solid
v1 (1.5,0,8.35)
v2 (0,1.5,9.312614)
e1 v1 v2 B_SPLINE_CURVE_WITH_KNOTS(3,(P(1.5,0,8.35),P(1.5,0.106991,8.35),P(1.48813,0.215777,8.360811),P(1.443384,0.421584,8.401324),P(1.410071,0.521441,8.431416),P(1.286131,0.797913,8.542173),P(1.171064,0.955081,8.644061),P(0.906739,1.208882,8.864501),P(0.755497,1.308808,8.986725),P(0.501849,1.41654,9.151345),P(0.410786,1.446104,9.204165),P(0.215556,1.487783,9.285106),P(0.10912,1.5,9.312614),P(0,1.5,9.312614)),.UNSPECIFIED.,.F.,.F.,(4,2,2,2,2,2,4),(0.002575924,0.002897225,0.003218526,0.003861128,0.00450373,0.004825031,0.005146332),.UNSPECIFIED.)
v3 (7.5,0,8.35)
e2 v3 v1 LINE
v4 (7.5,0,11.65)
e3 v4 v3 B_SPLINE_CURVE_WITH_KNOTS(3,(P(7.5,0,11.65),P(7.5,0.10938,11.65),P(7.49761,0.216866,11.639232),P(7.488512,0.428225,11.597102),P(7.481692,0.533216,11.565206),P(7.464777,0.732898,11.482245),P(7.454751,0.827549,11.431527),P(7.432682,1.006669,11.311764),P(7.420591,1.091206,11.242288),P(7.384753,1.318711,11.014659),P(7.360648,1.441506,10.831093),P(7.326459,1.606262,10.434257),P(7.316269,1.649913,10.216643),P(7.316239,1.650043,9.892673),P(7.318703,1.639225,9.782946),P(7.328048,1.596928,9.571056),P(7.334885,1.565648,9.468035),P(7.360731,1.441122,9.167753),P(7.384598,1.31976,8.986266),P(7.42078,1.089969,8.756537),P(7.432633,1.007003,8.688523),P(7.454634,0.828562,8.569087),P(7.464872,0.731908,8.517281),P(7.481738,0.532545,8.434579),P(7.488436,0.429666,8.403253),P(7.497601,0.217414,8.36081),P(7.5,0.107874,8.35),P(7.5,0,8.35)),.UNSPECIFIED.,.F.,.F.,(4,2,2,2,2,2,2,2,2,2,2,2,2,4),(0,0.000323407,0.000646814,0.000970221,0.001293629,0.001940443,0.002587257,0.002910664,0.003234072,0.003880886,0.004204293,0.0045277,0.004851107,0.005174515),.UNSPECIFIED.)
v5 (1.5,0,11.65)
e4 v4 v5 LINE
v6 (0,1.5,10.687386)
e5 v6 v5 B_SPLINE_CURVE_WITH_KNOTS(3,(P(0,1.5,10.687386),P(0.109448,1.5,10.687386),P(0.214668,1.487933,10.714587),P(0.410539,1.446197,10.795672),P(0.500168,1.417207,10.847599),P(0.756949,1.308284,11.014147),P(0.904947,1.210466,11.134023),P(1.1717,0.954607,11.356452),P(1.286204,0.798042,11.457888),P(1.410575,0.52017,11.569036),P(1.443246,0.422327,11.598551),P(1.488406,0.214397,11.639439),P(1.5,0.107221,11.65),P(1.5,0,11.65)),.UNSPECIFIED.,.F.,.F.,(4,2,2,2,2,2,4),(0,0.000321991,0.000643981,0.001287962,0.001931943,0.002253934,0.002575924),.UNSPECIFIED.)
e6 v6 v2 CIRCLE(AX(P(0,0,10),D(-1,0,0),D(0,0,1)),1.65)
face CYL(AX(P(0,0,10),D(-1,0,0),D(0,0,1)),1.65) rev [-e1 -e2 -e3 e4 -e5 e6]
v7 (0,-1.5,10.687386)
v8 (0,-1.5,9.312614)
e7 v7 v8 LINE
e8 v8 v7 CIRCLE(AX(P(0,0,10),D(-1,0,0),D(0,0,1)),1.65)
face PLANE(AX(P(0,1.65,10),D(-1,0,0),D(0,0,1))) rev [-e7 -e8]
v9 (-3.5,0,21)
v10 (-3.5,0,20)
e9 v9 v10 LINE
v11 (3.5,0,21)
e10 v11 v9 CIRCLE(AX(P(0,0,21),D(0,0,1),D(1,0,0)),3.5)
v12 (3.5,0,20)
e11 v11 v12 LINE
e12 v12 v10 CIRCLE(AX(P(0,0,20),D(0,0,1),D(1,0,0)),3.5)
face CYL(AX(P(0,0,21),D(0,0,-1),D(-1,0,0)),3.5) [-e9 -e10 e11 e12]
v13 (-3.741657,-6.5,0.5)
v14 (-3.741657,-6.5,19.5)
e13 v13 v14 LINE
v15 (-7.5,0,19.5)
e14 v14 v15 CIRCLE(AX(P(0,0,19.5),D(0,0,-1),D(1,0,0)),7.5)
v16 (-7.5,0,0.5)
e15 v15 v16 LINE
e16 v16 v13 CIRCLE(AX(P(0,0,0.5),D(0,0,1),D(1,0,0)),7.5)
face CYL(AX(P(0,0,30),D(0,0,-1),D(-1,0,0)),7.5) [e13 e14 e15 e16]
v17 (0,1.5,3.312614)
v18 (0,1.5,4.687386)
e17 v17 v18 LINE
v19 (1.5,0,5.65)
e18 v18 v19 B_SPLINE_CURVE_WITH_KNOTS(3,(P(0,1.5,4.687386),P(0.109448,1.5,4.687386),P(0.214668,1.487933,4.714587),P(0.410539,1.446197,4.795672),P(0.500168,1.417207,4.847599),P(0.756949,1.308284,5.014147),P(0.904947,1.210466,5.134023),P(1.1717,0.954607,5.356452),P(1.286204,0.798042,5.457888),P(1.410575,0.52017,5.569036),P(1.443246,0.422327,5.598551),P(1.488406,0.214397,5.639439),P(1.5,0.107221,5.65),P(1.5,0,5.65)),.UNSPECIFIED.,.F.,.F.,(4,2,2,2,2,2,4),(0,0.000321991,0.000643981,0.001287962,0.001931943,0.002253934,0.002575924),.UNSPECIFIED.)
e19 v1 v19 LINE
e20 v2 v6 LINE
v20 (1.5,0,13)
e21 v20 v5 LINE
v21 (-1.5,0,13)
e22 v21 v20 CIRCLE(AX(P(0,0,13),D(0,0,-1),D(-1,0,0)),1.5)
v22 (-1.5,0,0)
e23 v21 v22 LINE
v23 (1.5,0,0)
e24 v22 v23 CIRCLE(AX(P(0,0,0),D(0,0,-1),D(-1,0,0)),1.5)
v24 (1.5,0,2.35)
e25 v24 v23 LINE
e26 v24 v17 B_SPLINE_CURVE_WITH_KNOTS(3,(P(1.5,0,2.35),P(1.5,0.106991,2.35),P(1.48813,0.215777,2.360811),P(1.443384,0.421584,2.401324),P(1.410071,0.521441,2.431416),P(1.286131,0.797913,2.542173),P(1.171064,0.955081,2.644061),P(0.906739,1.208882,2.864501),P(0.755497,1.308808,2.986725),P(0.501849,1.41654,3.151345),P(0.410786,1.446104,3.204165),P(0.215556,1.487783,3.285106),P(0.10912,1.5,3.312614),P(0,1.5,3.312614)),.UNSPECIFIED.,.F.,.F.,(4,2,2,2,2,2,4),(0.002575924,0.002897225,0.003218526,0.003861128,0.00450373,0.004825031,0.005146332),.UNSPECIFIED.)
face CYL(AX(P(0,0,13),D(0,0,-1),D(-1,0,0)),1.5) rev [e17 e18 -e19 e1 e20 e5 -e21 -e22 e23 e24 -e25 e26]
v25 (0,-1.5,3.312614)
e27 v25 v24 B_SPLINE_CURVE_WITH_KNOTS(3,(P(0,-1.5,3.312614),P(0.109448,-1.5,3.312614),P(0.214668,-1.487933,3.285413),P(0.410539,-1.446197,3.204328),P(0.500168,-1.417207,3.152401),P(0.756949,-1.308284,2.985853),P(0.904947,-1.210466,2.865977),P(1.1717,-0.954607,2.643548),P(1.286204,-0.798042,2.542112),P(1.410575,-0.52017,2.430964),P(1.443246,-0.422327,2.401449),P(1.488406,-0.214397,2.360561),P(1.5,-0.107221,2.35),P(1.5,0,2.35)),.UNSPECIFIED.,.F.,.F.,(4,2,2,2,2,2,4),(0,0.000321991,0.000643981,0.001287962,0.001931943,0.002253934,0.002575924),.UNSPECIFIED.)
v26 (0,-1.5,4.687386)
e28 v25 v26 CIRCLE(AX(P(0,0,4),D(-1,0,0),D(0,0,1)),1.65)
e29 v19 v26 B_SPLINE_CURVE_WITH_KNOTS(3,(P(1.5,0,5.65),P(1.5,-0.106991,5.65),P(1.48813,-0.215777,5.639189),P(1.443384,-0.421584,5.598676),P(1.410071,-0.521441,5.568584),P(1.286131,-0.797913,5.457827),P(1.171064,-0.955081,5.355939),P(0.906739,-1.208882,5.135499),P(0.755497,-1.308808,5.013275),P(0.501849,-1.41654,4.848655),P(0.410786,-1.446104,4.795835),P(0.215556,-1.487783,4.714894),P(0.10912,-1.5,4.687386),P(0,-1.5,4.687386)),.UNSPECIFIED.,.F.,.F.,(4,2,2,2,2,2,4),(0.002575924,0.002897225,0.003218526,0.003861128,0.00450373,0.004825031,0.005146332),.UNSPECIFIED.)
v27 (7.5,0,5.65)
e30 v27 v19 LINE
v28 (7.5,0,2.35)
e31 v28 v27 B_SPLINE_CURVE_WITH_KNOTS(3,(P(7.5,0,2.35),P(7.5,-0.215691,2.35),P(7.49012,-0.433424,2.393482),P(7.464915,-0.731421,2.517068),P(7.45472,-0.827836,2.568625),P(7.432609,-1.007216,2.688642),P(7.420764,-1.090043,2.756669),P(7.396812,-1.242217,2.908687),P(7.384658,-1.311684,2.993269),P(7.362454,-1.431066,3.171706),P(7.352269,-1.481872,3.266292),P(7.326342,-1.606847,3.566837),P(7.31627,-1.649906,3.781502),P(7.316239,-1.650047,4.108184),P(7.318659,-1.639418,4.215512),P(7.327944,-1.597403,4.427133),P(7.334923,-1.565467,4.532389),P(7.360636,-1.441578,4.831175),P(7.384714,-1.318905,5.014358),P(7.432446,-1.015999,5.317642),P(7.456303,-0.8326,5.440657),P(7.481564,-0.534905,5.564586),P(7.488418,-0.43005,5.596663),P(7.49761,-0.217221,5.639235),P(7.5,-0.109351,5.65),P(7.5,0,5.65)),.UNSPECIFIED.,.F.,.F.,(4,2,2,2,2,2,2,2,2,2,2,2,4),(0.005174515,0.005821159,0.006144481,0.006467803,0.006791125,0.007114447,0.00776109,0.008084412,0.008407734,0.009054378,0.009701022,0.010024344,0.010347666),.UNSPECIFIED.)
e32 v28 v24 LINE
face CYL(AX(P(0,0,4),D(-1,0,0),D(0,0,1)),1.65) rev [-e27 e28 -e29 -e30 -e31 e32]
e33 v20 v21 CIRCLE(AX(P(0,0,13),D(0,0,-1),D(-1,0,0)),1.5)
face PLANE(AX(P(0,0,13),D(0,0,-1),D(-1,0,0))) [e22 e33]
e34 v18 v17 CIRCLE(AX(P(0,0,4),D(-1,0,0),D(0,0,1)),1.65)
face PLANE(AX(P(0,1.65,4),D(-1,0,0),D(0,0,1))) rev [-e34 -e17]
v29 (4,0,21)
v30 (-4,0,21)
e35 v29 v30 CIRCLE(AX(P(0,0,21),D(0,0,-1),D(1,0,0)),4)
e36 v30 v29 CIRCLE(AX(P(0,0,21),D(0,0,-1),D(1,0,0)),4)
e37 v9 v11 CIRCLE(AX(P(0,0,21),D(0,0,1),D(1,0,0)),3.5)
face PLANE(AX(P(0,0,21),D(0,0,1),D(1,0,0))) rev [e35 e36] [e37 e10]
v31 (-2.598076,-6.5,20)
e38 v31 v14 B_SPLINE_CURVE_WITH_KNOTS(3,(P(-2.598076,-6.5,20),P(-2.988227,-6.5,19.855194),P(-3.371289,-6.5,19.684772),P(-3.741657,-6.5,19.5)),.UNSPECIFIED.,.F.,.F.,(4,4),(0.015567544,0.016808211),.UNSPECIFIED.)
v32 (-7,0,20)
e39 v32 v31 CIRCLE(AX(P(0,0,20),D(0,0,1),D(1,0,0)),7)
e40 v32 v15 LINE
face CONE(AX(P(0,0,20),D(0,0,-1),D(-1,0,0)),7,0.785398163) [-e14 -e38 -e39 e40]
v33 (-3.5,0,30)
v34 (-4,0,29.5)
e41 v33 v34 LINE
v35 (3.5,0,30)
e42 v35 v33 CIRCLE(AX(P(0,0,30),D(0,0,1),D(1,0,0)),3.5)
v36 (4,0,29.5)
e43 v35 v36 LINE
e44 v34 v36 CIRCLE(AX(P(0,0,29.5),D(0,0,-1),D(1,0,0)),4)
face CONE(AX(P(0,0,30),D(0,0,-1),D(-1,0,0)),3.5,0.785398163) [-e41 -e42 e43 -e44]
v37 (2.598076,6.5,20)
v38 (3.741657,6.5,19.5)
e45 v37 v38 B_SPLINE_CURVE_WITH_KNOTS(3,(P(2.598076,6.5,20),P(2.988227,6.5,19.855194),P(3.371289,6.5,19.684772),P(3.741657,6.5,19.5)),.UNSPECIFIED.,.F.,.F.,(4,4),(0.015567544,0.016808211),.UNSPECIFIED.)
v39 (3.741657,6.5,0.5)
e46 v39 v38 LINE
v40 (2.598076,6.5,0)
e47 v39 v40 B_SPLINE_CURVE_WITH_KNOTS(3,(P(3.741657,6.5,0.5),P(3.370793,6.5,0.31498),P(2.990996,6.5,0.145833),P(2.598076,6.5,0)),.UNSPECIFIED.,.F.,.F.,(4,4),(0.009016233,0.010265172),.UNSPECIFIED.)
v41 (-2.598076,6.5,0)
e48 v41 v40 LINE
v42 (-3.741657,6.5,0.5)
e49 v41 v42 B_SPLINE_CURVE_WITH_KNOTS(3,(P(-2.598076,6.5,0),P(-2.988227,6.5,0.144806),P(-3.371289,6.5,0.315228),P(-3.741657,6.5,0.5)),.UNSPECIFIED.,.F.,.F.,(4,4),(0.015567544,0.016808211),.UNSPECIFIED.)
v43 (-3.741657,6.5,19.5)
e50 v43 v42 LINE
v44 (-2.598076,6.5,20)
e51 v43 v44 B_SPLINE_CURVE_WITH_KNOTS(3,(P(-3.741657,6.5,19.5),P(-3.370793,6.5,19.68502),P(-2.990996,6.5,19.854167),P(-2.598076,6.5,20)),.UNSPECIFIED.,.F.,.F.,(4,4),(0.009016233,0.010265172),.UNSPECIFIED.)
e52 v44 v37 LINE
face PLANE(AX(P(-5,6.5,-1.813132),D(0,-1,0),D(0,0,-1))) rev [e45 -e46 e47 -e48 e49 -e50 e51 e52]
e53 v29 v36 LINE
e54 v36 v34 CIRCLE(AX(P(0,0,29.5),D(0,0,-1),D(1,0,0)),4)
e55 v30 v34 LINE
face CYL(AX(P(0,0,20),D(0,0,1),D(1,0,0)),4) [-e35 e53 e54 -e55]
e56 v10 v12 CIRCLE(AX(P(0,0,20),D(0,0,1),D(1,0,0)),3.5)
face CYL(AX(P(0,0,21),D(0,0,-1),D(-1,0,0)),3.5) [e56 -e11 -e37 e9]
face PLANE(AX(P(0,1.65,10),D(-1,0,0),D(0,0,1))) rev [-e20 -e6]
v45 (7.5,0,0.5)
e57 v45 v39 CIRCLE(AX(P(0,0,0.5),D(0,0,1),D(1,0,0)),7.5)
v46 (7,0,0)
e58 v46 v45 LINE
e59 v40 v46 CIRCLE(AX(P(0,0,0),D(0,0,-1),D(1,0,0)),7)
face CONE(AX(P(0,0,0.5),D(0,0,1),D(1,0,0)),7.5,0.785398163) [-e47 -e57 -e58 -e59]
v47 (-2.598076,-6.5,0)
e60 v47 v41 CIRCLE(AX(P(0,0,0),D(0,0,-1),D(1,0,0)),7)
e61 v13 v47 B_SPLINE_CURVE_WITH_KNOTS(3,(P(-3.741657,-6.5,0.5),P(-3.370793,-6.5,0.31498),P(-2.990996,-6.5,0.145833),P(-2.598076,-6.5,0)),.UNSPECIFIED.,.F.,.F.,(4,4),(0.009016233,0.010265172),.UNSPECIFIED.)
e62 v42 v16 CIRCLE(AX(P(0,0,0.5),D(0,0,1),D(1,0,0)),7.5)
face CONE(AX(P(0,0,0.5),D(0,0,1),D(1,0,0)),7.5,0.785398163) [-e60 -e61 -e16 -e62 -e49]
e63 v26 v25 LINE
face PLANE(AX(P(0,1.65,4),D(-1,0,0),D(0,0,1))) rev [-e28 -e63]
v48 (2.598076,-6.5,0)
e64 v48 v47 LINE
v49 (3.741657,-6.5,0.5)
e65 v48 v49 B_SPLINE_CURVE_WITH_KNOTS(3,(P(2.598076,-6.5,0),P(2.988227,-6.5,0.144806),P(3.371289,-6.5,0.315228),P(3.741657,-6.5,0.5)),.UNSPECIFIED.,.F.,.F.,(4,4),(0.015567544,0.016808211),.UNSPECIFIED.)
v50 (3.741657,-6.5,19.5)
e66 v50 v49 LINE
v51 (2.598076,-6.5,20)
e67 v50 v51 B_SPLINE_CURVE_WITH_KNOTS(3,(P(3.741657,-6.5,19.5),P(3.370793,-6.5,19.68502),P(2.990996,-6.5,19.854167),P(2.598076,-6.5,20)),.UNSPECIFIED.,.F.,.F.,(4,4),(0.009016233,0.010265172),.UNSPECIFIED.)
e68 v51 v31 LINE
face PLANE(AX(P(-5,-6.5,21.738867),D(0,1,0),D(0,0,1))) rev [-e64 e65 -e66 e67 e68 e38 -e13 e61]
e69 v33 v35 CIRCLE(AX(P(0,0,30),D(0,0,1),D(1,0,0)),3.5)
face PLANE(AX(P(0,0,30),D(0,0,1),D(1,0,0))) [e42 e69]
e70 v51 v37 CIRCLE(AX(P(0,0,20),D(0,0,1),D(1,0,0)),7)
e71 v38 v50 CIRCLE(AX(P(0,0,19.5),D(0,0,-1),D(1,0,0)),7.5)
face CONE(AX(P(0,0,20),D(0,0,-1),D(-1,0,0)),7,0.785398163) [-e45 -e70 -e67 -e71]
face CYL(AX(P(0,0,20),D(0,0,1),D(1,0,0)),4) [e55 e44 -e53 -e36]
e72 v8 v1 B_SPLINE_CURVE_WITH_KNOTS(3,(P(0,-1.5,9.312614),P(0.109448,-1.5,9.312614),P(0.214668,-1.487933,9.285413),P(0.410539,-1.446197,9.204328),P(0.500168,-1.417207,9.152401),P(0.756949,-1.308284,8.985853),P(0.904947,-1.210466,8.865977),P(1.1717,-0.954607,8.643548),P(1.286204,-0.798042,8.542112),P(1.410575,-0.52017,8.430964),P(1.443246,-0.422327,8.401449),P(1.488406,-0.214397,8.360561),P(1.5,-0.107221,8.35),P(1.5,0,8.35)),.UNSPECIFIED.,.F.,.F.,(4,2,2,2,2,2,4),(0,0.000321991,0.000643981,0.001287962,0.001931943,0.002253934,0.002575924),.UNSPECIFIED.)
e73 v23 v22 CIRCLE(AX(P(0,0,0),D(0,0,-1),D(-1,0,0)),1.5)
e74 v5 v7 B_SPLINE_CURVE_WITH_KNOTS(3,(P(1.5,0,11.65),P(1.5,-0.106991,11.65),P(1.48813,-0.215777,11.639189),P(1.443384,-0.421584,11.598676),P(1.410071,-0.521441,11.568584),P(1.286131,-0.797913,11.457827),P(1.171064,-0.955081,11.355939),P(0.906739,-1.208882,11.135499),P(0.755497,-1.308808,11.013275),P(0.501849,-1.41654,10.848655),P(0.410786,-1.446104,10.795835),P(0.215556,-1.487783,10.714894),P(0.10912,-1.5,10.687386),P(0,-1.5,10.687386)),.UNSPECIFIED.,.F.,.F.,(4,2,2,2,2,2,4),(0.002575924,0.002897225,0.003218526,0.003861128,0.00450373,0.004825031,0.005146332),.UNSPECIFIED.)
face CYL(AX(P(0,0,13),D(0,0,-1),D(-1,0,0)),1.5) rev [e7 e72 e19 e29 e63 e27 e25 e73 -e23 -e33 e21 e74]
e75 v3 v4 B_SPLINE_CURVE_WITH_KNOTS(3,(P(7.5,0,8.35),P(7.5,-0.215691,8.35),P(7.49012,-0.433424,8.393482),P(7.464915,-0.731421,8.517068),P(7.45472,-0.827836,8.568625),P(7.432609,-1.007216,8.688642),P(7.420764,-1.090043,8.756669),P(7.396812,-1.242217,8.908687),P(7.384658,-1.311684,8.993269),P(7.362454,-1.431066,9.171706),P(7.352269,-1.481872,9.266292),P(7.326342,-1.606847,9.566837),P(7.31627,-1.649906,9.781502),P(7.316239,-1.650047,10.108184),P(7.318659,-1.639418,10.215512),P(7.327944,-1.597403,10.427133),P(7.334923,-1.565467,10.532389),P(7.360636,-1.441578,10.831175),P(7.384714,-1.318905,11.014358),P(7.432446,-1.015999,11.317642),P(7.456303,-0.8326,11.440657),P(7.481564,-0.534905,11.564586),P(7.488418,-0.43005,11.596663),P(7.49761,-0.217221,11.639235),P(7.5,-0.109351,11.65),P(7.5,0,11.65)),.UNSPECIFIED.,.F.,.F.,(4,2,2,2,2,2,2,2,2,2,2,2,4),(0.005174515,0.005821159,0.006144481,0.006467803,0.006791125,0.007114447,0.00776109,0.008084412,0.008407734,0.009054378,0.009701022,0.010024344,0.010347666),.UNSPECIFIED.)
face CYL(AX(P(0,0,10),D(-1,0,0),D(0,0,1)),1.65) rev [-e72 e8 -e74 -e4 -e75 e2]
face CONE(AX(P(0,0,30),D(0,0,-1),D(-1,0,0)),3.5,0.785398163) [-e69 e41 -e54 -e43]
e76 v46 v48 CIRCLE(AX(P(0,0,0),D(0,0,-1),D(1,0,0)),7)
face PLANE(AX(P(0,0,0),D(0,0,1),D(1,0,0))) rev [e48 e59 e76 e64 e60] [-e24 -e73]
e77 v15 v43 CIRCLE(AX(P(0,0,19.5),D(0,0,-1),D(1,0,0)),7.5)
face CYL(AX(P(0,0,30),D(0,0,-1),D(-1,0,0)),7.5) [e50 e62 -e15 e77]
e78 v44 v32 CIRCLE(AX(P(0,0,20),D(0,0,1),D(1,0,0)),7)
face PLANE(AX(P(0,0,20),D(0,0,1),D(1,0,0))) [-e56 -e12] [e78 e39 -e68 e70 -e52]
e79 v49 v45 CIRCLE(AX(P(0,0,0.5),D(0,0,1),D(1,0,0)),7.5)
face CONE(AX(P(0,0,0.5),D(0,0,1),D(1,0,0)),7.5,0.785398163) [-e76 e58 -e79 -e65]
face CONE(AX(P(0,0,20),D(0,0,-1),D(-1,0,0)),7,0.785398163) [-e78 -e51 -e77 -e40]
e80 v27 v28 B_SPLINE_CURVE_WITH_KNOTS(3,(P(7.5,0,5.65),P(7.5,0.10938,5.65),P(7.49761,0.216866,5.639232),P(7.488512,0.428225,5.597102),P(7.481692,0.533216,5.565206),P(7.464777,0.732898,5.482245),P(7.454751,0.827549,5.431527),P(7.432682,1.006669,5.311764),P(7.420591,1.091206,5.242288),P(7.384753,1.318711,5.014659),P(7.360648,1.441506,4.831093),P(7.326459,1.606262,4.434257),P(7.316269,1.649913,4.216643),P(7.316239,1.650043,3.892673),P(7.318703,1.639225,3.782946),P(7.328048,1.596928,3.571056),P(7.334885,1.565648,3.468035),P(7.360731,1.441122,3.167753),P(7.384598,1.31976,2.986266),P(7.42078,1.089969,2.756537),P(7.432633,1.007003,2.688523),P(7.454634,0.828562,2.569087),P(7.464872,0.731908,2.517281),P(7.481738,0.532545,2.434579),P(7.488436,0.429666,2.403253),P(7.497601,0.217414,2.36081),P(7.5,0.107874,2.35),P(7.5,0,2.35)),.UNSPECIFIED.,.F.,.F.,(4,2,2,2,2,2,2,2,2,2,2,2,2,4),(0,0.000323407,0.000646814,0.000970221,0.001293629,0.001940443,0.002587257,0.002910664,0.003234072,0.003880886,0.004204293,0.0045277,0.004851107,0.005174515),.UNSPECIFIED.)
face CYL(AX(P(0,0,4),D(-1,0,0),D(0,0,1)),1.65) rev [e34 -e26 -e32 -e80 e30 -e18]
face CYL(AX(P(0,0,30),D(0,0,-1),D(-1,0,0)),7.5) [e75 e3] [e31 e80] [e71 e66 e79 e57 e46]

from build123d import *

# Parameters (mm, degrees)
SKETCH_1_R                  = 7.5
EXTRUDE_1_DEPTH             = 30
SKETCH_2_R                  = 8.226284638
SKETCH_2_R_2                = 4
CUT_EXTRUDE_1_DEPTH         = 10
SKETCH_3_R                  = 1.5
CUT_EXTRUDE_2_DEPTH         = 13
SKETCH_4_R                  = 4.479492859
SKETCH_4_R_2                = 3.5
CUT_EXTRUDE_3_DEPTH         = 1
CHAMFER_1_SIZE              = 0.5
SKETCH_6_W                  = 1.65
SKETCH_6_H                  = 7.5
HOLE_WIZARD_M4_1_AT_2_COUNT = 2
HOLE_WIZARD_M4_1_AT_2_PITCH = 6
SKETCH_7_W                  = 26.910087363
SKETCH_7_H                  = 4.855614415
SKETCH_7_W_2                = 23.143582724
SKETCH_7_H_2                = 3.131190604
CUT_EXTRUDE_4_DEPTH         = 5


with BuildPart() as part:
    # 草图1 → 凸台-拉伸1 (new body)
    with BuildSketch(Plane.XY):
        Circle(SKETCH_1_R)
    extrude(amount=EXTRUDE_1_DEPTH)

    # 草图2 → 切除-拉伸1 (cut)
    with BuildSketch(Plane.XY.offset(30)):
        Circle(SKETCH_2_R)
        Circle(SKETCH_2_R_2, mode=Mode.SUBTRACT)
    extrude(amount=-CUT_EXTRUDE_1_DEPTH, mode=Mode.SUBTRACT)

    # 草图3 → 切除-拉伸2 (cut)
    with BuildSketch(Plane(origin=(0, 0, 0), x_dir=(-1, 0, 0), z_dir=(0, 0, -1))):
        Circle(SKETCH_3_R)
    extrude(amount=-CUT_EXTRUDE_2_DEPTH, mode=Mode.SUBTRACT)

    # 草图4 → 切除-拉伸3 (cut)
    with BuildSketch(Plane.XY.offset(20)):
        Circle(SKETCH_4_R)
        Circle(SKETCH_4_R_2, mode=Mode.SUBTRACT)
    extrude(amount=CUT_EXTRUDE_3_DEPTH, mode=Mode.SUBTRACT)

    # 倒角1
    chamfer_1_edges = [part.edges().sort_by_distance(p)[0] for p in [
        (-7.5, 0, 0),
        (-7.5, 0, 20),
        (-4, 0, 30),
    ]]
    chamfer(chamfer_1_edges, length=CHAMFER_1_SIZE)

    # 草图6 → M4 螺纹孔1 (revolve, cut)
    with BuildSketch(Plane(origin=(0, 0, 4), x_dir=(0, 0, 1), z_dir=(0, 1, 0))):
        with Locations((0.825, 3.75)):
            Rectangle(SKETCH_6_W, SKETCH_6_H)
    hole_wizard_m4_1 = revolve(axis=Axis((-6.35, 0, 4), (1, 0, 0)), mode=Mode.SUBTRACT)

    # M4 螺纹孔1 at 2: M4 螺纹孔1 ×2
    with Locations(*[(0, 0, i * HOLE_WIZARD_M4_1_AT_2_PITCH) for i in range(1, HOLE_WIZARD_M4_1_AT_2_COUNT)]):
        add(hole_wizard_m4_1, mode=Mode.SUBTRACT)

    # 草图7 → 切除-拉伸4 (cut, symmetric)
    with BuildSketch(Plane(origin=(0, 0, 0), x_dir=(0, 0, -1), z_dir=(1, 0, 0))):
        with Locations((-11.641911526, 8.927807208)):
            Rectangle(SKETCH_7_W, SKETCH_7_H)
        with Locations((-10.167075372, -8.065595302)):
            Rectangle(SKETCH_7_W_2, SKETCH_7_H_2)
    extrude(amount=CUT_EXTRUDE_4_DEPTH, both=True, mode=Mode.SUBTRACT)


solid = part.part
